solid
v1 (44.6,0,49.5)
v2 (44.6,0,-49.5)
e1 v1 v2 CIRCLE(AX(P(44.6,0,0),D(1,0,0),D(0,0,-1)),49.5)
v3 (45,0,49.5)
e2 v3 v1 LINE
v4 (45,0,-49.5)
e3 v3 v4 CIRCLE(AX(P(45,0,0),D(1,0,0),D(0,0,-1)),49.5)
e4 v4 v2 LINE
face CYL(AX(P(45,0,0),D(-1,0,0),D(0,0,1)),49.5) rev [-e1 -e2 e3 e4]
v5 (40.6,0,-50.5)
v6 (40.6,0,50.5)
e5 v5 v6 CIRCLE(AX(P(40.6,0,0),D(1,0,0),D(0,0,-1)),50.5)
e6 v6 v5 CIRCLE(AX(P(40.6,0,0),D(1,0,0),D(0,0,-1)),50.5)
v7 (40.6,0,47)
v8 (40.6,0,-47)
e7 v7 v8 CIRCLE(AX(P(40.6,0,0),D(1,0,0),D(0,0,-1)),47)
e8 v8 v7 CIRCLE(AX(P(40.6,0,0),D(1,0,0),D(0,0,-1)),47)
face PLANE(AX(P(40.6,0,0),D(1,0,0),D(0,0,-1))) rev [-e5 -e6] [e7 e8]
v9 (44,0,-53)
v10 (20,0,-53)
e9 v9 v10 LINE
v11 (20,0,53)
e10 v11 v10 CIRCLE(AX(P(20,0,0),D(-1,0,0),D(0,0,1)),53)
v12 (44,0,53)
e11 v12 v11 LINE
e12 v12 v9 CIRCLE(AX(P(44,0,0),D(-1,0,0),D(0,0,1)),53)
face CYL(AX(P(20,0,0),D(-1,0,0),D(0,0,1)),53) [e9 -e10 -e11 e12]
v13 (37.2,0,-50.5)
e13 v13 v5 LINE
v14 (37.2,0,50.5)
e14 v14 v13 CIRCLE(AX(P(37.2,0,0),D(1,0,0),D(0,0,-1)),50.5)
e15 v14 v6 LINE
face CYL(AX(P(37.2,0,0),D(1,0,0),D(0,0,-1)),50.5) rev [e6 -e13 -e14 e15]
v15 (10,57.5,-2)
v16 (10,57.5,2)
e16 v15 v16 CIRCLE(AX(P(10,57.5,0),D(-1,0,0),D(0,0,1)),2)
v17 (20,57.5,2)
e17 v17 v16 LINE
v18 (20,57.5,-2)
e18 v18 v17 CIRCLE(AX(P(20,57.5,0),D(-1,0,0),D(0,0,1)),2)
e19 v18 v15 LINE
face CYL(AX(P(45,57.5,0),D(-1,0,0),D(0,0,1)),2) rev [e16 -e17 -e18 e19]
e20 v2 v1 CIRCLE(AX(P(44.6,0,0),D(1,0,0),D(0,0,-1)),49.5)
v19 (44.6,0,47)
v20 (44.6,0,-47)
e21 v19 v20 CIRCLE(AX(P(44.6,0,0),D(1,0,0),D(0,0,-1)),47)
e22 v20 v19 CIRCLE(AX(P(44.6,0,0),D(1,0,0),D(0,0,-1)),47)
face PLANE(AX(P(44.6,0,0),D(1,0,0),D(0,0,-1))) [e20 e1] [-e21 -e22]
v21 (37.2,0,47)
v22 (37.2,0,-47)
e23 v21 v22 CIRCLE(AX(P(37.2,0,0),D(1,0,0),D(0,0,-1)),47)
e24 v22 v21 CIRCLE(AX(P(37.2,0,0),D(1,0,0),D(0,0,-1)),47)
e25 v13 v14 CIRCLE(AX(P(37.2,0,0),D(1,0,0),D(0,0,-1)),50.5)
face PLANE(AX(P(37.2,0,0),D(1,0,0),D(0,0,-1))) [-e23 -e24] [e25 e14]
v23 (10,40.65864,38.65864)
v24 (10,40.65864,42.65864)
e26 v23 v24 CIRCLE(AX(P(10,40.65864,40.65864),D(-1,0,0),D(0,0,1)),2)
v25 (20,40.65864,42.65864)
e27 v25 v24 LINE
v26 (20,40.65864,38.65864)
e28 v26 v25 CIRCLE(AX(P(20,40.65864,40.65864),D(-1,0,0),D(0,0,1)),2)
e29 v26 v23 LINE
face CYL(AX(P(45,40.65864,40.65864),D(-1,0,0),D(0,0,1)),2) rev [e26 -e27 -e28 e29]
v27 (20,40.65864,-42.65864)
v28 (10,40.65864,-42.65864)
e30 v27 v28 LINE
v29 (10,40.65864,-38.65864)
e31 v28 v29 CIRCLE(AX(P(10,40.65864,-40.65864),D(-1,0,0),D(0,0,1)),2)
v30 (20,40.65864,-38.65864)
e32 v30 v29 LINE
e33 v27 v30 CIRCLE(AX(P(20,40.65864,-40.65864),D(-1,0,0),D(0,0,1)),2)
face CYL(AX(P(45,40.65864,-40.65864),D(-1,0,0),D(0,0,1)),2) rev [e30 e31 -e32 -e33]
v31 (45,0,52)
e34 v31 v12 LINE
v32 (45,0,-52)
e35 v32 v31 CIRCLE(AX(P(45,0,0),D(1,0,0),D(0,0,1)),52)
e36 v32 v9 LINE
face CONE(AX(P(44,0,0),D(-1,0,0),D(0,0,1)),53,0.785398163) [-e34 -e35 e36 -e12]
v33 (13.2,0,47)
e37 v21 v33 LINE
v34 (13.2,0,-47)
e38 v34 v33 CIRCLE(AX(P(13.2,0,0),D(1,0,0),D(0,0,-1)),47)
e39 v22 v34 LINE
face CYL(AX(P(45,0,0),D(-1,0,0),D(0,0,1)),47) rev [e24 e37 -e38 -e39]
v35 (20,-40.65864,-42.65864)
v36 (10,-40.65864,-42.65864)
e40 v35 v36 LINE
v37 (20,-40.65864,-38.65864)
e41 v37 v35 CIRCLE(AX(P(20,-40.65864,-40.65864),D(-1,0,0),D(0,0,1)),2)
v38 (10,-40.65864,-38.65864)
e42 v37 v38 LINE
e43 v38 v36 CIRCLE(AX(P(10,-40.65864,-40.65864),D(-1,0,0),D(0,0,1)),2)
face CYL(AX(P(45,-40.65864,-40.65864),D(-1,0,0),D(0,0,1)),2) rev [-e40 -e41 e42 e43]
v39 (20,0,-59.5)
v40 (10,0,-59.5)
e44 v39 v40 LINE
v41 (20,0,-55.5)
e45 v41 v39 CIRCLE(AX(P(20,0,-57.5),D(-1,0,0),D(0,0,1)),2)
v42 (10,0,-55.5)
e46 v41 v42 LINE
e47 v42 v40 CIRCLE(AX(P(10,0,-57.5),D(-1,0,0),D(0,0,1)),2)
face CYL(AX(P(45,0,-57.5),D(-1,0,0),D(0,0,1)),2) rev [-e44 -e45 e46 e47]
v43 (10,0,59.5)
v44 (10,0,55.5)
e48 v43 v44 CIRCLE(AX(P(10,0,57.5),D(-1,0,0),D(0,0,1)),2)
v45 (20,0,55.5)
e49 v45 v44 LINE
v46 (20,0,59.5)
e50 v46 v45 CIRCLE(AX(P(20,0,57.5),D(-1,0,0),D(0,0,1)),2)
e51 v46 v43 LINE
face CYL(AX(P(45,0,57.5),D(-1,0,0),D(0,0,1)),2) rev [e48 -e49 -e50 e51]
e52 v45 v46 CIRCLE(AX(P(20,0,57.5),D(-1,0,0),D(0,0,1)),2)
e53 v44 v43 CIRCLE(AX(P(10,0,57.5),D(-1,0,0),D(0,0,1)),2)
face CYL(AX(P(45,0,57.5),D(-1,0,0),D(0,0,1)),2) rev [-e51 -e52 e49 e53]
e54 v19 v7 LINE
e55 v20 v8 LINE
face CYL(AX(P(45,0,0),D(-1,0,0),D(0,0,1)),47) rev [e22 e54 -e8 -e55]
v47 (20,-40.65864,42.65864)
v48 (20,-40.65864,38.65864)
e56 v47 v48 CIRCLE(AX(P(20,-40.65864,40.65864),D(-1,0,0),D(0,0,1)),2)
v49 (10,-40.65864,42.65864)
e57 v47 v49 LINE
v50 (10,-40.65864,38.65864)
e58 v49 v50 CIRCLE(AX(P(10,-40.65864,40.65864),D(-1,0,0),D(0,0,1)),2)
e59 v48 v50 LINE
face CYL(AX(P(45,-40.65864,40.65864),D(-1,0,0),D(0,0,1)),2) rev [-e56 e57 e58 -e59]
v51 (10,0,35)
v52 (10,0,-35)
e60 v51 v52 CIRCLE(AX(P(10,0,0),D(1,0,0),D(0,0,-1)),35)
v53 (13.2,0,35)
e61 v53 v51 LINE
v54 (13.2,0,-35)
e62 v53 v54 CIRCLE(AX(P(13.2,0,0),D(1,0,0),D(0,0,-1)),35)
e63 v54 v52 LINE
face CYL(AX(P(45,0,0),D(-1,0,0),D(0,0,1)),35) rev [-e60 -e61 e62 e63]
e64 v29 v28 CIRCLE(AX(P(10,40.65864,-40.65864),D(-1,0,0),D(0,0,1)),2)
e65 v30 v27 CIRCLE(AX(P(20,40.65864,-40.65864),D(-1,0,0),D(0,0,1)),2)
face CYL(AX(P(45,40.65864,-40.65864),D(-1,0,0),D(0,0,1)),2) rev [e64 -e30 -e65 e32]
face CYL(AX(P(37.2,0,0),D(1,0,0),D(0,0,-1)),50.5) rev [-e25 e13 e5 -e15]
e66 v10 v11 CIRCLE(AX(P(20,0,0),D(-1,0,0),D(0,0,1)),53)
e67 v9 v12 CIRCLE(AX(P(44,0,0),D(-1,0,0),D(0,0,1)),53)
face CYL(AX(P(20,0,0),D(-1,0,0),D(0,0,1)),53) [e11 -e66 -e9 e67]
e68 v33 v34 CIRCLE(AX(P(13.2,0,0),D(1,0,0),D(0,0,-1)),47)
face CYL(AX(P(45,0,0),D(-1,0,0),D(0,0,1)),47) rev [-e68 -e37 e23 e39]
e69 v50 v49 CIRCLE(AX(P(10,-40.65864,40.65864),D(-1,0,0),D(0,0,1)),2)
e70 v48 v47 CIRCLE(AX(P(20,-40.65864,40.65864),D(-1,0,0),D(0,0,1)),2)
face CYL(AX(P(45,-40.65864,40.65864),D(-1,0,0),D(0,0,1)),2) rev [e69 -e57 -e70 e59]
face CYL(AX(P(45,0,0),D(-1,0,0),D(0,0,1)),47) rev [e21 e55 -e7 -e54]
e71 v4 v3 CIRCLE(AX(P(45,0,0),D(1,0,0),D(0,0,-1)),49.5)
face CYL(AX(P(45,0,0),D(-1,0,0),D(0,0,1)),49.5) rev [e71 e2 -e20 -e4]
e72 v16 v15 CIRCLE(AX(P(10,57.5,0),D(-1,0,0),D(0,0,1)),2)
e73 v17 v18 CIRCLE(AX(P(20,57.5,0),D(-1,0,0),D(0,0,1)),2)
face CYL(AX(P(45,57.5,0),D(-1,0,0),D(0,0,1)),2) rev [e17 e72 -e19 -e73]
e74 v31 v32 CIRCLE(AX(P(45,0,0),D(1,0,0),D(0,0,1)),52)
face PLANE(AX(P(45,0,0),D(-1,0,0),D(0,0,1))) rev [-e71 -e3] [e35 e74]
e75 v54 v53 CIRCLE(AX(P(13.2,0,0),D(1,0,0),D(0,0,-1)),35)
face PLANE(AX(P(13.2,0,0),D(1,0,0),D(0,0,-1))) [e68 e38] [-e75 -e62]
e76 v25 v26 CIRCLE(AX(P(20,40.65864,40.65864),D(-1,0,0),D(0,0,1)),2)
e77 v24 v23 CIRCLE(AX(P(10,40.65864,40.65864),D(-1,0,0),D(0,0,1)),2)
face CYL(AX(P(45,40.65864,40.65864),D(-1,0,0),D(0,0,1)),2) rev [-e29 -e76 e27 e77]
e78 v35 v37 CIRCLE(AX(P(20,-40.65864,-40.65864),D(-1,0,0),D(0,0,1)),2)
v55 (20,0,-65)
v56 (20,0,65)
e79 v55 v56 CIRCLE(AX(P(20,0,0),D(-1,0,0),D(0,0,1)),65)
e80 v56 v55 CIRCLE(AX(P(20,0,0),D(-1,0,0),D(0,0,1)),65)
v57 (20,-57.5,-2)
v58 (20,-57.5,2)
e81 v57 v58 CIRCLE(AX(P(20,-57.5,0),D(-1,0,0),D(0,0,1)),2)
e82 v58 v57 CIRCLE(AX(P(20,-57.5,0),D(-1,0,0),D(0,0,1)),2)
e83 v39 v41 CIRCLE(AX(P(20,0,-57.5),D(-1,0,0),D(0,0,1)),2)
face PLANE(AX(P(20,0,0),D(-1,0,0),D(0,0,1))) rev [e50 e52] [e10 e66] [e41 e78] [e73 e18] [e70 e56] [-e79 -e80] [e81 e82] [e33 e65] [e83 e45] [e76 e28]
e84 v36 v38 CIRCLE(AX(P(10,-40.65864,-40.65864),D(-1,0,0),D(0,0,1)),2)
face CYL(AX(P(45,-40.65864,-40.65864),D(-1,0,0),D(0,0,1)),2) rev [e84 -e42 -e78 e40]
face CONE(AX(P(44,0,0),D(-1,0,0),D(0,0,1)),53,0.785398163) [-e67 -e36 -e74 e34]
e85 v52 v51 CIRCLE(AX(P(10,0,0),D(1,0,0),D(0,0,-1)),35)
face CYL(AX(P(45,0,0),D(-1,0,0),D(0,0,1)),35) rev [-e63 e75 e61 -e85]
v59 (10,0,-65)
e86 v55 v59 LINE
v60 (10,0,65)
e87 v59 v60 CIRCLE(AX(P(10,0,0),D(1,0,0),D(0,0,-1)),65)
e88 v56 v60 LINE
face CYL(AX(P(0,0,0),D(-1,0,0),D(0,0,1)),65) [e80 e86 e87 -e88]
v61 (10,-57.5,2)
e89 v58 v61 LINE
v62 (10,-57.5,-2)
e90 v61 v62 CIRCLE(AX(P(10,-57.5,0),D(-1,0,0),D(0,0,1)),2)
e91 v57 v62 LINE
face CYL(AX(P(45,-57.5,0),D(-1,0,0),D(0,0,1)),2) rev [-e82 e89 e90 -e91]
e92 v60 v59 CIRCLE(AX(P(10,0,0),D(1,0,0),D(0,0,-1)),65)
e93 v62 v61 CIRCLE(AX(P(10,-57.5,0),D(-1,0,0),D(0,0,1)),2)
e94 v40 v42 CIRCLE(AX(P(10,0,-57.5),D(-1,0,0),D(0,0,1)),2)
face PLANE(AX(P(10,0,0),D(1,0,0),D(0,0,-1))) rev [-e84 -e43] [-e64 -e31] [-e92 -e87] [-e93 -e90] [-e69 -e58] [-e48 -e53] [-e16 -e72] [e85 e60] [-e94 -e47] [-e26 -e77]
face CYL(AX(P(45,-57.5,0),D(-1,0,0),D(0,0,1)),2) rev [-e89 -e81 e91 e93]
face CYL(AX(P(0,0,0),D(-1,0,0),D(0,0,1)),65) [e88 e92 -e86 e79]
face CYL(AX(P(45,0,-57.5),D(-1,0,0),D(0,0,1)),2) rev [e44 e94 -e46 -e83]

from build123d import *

# Parameters (mm, degrees)
SKETCH_2_W          = 20
SKETCH_2_H          = 65
SKETCH_3_W          = 25
SKETCH_3_H          = 53
SKETCH_6_R          = 35
CUT_EXTRUDE_1_DEPTH = 103.347447452
CUT_EXTRUDE_START   = 13.2
SKETCH_7_R          = 47
CUT_EXTRUDE_2_DEPTH = 90.147447452
CUT_EXTRUDE_START_2 = 40.6
SKETCH_10_R         = 50.5
CUT_EXTRUDE_4_DEPTH = 3.4
SKETCH_15_R         = 65
CUT_EXTRUDE_6_DEPTH = 10
CUT_EXTRUDE_START_3 = 44.6
SKETCH_12_R         = 49.5
CUT_EXTRUDE_5_DEPTH = 58.747447452
SKETCH_16_R         = 2
CUT_EXTRUDE_7_DEPTH = 99.361577865
CHAMFER_1_SIZE      = 1


with BuildPart() as part:
    # 草图2 → 旋转-薄壁1 (revolve)
    with BuildSketch(Plane.XY, mode=Mode.PRIVATE) as revolve_1_sk:
        with Locations((10, 32.5)):
            Rectangle(SKETCH_2_W, SKETCH_2_H)
    revolve(revolve_1_sk.sketch.rotate(Axis((0, 0, 0), (1, 0, 0)), 90), axis=Axis((0, 0, 0), (1, 0, 0)))

    # 草图3 → 旋转-薄壁2 (revolve)
    with BuildSketch(Plane.XY, mode=Mode.PRIVATE) as revolve_2_sk:
        with Locations((32.5, 26.5)):
            Rectangle(SKETCH_3_W, SKETCH_3_H)
    revolve(revolve_2_sk.sketch.rotate(Axis((20, 0, 0), (1, 0, 0)), 90), axis=Axis((20, 0, 0), (1, 0, 0)))

    # 草图6 → 切除-拉伸1 (cut, through all)
    with BuildSketch(Plane(origin=(0, 0, 0), x_dir=(0, 0, -1), z_dir=(1, 0, 0))):
        with Locations(Location((0, 0, 0), (0, 0, 180))):
            Circle(SKETCH_6_R)
    extrude(amount=CUT_EXTRUDE_1_DEPTH, mode=Mode.SUBTRACT)

    # 草图7 → 切除-拉伸2 (cut, through all)
    with BuildSketch(Plane(origin=(0, 0, 0), x_dir=(0, 0, -1), z_dir=(1, 0, 0)).offset(CUT_EXTRUDE_START)):
        Circle(SKETCH_7_R)
    extrude(amount=CUT_EXTRUDE_2_DEPTH, mode=Mode.SUBTRACT)

    # 草图10 → 切除-拉伸4 (cut)
    with BuildSketch(Plane(origin=(0, 0, 0), x_dir=(0, 0, -1), z_dir=(1, 0, 0)).offset(CUT_EXTRUDE_START_2)):
        Circle(SKETCH_10_R)
    extrude(amount=-CUT_EXTRUDE_4_DEPTH, mode=Mode.SUBTRACT)

    # 草图15 → 切除-拉伸6 (cut)
    with BuildSketch(Plane(origin=(0, 0, 0), x_dir=(0, 0, -1), z_dir=(1, 0, 0))):
        with Locations(Location((0, 0, 0), (0, 0, 180))):
            Circle(SKETCH_15_R)
    extrude(amount=CUT_EXTRUDE_6_DEPTH, mode=Mode.SUBTRACT)

    # 草图12 → 切除-拉伸5 (cut, through all)
    with BuildSketch(Plane(origin=(0, 0, 0), x_dir=(0, 0, -1), z_dir=(1, 0, 0)).offset(CUT_EXTRUDE_START_3)):
        Circle(SKETCH_12_R)
    extrude(amount=CUT_EXTRUDE_5_DEPTH, mode=Mode.SUBTRACT)

    # 草图16 → 切除-拉伸7 (cut, through all)
    with BuildSketch(Plane.ZY.offset(-10)):
        with Locations((0, 57.5)):
            Circle(SKETCH_16_R)
        with Locations((40.658639918, 40.658639918)):
            Circle(SKETCH_16_R)
        with Locations((57.5, 0)):
            Circle(SKETCH_16_R)
        with Locations((40.658639918, -40.658639918)):
            Circle(SKETCH_16_R)
        with Locations((0, -57.5)):
            Circle(SKETCH_16_R)
        with Locations((-40.658639918, -40.658639918)):
            Circle(SKETCH_16_R)
        with Locations((-57.5, 0)):
            Circle(SKETCH_16_R)
        with Locations((-40.658639918, 40.658639918)):
            Circle(SKETCH_16_R)
    extrude(amount=-CUT_EXTRUDE_7_DEPTH, mode=Mode.SUBTRACT)

    # 倒角1
    chamfer_1_edges = [part.edges().sort_by_distance(p)[0] for p in [
        (45, 0, -53),
    ]]
    chamfer(chamfer_1_edges, length=CHAMFER_1_SIZE)


solid = part.part
